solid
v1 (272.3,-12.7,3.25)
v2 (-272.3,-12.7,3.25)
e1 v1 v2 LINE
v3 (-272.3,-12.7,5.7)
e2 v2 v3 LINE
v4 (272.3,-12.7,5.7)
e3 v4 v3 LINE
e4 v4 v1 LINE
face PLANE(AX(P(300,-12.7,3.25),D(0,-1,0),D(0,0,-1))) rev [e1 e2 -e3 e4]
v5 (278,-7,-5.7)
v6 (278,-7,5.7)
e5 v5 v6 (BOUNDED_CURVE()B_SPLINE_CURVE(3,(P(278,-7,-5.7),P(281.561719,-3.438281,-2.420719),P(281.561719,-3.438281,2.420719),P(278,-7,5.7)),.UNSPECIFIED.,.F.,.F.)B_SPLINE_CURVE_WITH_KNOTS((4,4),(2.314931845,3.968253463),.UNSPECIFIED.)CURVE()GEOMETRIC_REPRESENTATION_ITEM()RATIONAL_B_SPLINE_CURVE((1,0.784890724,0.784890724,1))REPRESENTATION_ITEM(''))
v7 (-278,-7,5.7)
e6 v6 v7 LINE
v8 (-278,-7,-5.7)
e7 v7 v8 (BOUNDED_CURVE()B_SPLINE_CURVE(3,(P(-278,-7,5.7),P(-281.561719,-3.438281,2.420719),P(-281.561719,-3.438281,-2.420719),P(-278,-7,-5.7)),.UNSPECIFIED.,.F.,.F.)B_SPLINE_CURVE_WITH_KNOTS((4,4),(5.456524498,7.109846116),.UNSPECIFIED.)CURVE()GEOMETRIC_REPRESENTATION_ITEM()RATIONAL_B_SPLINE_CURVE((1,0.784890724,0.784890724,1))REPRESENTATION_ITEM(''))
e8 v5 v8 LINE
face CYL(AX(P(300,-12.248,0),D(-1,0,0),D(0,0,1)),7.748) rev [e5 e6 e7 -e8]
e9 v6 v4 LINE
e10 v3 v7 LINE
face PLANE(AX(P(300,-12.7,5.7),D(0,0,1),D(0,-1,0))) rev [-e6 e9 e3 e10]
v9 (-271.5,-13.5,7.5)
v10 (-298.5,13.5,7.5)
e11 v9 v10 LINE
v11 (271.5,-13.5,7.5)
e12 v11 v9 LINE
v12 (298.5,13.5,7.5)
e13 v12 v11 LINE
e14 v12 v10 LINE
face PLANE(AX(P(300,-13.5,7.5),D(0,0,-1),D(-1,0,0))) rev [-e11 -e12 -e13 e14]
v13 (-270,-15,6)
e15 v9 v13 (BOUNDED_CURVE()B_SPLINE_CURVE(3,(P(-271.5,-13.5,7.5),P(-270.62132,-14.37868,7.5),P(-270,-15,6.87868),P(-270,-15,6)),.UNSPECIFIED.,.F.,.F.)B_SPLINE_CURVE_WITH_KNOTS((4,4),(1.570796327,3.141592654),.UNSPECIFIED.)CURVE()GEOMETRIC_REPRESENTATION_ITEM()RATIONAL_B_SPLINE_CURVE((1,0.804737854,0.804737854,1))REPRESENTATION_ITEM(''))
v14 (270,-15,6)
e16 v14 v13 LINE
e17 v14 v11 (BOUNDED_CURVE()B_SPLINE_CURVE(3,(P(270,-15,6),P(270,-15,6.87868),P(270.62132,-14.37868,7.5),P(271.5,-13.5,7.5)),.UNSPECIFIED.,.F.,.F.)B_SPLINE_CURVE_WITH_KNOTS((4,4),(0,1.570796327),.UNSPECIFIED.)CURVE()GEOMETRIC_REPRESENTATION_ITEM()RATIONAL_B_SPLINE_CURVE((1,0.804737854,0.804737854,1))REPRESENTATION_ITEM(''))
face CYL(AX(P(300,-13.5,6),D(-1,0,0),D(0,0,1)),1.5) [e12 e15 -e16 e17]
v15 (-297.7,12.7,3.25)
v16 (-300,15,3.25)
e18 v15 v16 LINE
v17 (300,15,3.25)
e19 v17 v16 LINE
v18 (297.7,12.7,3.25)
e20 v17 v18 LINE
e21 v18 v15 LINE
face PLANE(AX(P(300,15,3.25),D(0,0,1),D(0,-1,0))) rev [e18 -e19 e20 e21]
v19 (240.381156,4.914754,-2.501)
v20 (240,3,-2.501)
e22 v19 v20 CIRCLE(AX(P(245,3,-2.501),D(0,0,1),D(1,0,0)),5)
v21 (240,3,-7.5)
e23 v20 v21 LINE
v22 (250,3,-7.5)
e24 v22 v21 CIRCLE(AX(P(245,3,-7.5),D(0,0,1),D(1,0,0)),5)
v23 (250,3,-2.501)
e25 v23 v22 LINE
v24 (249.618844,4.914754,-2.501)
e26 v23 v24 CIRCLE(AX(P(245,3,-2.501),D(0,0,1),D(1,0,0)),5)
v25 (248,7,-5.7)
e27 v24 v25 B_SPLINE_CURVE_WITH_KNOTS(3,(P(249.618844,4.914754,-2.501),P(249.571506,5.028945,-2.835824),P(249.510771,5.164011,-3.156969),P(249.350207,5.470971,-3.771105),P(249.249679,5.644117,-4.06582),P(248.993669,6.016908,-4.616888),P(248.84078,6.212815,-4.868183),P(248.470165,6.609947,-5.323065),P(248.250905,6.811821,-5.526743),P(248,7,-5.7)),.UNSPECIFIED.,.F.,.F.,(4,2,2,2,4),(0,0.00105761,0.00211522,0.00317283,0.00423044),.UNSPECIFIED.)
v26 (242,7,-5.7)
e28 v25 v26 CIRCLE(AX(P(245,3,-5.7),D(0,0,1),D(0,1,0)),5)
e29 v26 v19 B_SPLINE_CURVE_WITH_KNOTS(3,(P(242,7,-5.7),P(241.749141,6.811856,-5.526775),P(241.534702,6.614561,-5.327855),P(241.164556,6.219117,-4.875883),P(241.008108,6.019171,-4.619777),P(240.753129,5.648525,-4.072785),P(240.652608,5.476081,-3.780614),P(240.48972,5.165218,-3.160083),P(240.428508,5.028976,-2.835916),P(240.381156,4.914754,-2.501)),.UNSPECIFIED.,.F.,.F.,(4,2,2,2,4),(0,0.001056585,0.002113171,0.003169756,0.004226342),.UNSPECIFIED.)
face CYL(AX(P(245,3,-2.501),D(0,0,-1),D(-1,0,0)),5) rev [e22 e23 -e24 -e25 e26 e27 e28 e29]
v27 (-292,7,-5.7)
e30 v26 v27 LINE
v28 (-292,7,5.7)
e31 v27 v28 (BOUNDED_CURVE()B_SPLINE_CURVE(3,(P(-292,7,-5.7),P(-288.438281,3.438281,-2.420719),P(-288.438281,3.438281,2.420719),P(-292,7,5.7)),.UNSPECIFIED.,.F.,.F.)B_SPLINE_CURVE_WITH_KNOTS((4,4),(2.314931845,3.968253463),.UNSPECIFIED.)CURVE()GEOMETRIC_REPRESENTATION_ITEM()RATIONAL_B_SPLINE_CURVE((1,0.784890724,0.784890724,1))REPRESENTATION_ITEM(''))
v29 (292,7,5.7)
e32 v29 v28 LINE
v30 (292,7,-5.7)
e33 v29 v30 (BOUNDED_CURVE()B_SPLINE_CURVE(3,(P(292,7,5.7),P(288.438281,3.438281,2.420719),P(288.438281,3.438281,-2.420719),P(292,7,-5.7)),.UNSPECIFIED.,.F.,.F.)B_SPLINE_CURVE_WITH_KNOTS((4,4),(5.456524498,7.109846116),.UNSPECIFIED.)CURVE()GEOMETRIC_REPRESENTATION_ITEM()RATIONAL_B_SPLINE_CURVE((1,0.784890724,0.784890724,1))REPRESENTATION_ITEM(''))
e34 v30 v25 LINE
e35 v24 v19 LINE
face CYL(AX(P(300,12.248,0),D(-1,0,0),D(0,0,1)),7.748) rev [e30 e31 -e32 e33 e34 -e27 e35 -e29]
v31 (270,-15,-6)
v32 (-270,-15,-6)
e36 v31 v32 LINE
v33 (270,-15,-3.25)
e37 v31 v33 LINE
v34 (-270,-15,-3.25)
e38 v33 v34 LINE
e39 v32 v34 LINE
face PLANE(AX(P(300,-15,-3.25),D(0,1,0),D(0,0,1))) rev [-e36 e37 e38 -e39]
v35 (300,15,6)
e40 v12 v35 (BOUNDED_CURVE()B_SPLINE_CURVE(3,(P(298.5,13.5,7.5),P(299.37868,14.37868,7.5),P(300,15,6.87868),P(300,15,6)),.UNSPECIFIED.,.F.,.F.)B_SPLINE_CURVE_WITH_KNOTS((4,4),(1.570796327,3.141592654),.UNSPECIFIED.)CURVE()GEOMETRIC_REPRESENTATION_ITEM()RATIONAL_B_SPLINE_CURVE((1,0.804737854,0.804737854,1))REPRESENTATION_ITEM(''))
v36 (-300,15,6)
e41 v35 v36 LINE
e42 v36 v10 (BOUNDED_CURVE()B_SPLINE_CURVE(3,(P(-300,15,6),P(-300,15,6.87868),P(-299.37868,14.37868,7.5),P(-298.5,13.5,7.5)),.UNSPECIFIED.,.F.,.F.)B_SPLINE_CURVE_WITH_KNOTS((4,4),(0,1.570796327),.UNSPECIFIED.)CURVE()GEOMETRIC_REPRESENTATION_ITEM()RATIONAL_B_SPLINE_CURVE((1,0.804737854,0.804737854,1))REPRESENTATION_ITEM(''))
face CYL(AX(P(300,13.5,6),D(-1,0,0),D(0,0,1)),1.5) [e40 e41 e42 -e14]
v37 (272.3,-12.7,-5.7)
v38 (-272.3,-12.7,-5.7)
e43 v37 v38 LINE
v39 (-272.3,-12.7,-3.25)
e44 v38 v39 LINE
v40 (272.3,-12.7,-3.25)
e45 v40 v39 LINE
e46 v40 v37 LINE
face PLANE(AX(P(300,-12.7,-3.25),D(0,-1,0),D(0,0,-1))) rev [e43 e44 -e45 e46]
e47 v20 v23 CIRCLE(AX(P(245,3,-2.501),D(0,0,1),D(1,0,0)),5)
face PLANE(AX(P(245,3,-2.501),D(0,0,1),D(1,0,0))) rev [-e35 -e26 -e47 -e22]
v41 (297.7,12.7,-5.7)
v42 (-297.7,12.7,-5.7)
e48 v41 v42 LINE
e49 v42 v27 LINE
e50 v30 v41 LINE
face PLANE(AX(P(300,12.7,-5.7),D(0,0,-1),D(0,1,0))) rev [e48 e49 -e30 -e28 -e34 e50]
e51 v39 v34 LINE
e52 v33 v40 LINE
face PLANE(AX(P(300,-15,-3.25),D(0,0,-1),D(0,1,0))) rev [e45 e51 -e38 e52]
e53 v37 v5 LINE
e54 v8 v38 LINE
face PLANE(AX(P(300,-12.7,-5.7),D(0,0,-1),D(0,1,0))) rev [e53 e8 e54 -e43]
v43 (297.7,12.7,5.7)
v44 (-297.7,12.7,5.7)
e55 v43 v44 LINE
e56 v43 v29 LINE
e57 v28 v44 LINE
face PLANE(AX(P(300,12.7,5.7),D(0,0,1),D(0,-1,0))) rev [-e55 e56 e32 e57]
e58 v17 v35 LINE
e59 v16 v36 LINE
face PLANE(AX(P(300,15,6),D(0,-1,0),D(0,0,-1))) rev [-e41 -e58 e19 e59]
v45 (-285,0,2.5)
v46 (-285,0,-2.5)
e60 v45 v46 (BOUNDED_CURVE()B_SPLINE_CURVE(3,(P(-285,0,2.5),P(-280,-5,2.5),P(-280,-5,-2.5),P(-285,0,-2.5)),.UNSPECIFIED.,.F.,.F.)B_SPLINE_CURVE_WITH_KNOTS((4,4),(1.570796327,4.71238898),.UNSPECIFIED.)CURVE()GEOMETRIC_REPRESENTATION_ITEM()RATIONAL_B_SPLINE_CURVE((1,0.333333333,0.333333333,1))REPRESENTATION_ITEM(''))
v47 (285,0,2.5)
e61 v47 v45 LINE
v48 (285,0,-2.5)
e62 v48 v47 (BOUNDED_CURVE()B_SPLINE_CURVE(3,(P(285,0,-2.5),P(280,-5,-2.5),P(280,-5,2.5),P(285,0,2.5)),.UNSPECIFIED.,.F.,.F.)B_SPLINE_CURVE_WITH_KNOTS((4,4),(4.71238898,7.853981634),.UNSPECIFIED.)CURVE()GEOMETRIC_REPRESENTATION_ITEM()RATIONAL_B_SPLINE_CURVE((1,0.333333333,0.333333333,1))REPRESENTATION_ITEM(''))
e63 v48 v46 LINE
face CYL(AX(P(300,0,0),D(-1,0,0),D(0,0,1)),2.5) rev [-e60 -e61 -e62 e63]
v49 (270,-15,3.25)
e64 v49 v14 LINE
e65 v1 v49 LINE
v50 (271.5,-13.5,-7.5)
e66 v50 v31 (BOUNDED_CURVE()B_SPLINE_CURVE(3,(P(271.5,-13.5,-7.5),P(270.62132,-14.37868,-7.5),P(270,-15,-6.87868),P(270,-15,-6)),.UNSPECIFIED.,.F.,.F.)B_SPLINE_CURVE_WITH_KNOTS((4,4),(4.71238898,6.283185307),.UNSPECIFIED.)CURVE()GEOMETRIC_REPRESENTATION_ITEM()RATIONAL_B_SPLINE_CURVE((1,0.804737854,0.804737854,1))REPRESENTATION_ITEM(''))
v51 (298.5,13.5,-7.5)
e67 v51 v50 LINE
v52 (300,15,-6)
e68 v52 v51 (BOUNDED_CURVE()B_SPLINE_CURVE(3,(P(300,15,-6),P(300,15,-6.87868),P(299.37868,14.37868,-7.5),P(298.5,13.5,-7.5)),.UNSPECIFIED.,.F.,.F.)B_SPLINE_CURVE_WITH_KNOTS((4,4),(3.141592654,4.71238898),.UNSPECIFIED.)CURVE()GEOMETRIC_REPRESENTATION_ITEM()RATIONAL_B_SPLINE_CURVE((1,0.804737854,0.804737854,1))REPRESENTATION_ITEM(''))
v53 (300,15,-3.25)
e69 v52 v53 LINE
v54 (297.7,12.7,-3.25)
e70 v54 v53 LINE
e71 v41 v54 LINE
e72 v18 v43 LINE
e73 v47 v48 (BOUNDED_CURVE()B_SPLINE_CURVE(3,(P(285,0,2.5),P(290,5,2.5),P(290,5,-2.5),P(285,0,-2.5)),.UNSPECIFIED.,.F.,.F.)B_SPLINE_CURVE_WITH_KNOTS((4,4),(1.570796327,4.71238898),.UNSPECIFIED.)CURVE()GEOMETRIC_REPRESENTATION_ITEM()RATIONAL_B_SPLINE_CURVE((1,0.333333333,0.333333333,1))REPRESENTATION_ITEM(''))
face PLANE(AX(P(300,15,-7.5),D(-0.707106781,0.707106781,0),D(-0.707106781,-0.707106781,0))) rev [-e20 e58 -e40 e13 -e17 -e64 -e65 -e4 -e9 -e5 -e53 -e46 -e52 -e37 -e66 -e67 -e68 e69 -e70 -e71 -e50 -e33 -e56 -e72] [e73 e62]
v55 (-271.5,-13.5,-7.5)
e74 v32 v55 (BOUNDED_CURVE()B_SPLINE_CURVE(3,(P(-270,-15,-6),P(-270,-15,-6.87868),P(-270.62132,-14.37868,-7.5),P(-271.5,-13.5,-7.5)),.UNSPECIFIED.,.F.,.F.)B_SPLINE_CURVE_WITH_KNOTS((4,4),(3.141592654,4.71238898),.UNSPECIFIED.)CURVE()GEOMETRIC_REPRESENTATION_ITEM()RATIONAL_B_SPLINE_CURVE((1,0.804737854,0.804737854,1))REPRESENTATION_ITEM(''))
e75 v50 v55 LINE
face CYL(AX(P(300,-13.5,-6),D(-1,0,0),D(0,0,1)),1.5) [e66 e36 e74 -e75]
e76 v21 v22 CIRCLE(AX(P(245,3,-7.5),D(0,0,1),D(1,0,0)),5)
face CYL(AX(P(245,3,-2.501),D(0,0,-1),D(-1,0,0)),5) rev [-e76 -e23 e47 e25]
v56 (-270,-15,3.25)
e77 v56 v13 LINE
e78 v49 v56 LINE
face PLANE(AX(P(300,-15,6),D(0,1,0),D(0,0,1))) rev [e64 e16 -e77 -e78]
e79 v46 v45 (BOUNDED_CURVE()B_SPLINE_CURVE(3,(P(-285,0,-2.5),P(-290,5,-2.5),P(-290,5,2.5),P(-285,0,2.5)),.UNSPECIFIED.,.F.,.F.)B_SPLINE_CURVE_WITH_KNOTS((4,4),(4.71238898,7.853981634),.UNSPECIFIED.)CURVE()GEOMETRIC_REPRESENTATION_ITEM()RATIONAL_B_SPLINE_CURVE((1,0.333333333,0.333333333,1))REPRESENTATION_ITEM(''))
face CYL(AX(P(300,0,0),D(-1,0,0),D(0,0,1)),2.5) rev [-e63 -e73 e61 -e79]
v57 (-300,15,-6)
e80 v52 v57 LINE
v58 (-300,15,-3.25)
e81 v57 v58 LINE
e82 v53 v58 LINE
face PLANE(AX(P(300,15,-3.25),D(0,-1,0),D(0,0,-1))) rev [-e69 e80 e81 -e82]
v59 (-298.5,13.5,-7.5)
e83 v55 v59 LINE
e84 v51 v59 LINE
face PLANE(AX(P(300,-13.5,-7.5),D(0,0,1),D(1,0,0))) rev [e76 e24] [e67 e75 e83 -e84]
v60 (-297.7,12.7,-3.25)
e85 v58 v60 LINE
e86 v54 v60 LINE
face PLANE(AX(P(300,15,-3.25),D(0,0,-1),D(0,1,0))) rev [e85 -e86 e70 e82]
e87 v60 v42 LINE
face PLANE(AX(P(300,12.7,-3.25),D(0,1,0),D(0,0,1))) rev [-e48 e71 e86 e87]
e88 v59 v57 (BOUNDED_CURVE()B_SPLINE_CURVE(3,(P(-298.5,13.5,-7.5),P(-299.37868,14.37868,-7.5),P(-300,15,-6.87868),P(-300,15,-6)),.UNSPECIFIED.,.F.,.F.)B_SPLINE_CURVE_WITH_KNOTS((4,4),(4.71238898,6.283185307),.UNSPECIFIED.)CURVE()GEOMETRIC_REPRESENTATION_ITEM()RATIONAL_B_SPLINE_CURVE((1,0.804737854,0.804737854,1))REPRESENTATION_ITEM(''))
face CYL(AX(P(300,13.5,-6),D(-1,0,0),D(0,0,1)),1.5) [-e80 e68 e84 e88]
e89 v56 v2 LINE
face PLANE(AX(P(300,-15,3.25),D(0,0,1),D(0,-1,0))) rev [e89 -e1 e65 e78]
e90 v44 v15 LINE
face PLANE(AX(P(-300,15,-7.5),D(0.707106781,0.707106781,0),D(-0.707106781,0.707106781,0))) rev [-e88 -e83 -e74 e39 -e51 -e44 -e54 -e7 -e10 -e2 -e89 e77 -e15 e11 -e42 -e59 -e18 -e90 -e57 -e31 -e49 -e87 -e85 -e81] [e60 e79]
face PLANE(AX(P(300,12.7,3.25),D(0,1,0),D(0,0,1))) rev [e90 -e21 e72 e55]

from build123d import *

# Parameters (mm, degrees)
SKETCH12_R          = 2.5
MEMBER_1_DEPTH      = 600
CUT_EXTRUDE_1_DEPTH = 301.749064836
SKETCH_7_R          = 5
CUT_EXTRUDE_2_DEPTH = 4.999


with BuildPart() as part:
    # Sketch12 → Member 1 (new body)
    with BuildSketch(Plane(origin=(-300, 0, 0), x_dir=(0, 0, -1), z_dir=(1, 0, 0))):
        with BuildLine():
            Line((-6, -15), (-3.25, -15))
            Line((-3.25, -15), (-3.25, -12.7))
            Line((-3.25, -12.7), (-5.7, -12.7))
            Line((-5.7, -12.7), (-5.7, -7))
            ThreePointArc((-5.7, -7), (0, -4.5), (5.7, -7))
            Line((5.7, -7), (5.7, -12.7))
            Line((5.7, -12.7), (3.25, -12.7))
            Line((3.25, -12.7), (3.25, -15))
            Line((3.25, -15), (6, -15))
            ThreePointArc((6, -15), (7.060660172, -14.560660172), (7.5, -13.5))
            Line((7.5, -13.5), (7.5, 13.5))
            ThreePointArc((7.5, 13.5), (7.060660172, 14.560660172), (6, 15))
            Line((6, 15), (3.25, 15))
            Line((3.25, 15), (3.25, 12.7))
            Line((3.25, 12.7), (5.7, 12.7))
            Line((5.7, 12.7), (5.7, 7))
            ThreePointArc((5.7, 7), (0, 4.5), (-5.7, 7))
            Line((-5.7, 7), (-5.7, 12.7))
            Line((-5.7, 12.7), (-3.25, 12.7))
            Line((-3.25, 12.7), (-3.25, 15))
            Line((-3.25, 15), (-6, 15))
            ThreePointArc((-6, 15), (-7.060660172, 14.560660172), (-7.5, 13.5))
            Line((-7.5, 13.5), (-7.5, -13.5))
            ThreePointArc((-7.5, -13.5), (-7.060660172, -14.560660172), (-6, -15))
        make_face()
        Circle(SKETCH12_R, mode=Mode.SUBTRACT)
    extrude(amount=MEMBER_1_DEPTH)

    # 草图4 → 切除-拉伸1 (cut, through all)
    with BuildSketch(Plane.XY.offset(7.5)):
        Polygon((-300, 15), (-270, -15), (-300, -15), align=None)
        Polygon((300, -15), (300, 15), (270, -15), align=None)
    extrude(amount=-CUT_EXTRUDE_1_DEPTH, mode=Mode.SUBTRACT)

    # 草图7 → 切除-拉伸2 (cut)
    with BuildSketch(Plane.XY.offset(-7.5)):
        with Locations(Location((245, 3, 0), (0, 0, 157.483422962))):
            Circle(SKETCH_7_R)
    extrude(amount=CUT_EXTRUDE_2_DEPTH, mode=Mode.SUBTRACT)


solid = part.part
